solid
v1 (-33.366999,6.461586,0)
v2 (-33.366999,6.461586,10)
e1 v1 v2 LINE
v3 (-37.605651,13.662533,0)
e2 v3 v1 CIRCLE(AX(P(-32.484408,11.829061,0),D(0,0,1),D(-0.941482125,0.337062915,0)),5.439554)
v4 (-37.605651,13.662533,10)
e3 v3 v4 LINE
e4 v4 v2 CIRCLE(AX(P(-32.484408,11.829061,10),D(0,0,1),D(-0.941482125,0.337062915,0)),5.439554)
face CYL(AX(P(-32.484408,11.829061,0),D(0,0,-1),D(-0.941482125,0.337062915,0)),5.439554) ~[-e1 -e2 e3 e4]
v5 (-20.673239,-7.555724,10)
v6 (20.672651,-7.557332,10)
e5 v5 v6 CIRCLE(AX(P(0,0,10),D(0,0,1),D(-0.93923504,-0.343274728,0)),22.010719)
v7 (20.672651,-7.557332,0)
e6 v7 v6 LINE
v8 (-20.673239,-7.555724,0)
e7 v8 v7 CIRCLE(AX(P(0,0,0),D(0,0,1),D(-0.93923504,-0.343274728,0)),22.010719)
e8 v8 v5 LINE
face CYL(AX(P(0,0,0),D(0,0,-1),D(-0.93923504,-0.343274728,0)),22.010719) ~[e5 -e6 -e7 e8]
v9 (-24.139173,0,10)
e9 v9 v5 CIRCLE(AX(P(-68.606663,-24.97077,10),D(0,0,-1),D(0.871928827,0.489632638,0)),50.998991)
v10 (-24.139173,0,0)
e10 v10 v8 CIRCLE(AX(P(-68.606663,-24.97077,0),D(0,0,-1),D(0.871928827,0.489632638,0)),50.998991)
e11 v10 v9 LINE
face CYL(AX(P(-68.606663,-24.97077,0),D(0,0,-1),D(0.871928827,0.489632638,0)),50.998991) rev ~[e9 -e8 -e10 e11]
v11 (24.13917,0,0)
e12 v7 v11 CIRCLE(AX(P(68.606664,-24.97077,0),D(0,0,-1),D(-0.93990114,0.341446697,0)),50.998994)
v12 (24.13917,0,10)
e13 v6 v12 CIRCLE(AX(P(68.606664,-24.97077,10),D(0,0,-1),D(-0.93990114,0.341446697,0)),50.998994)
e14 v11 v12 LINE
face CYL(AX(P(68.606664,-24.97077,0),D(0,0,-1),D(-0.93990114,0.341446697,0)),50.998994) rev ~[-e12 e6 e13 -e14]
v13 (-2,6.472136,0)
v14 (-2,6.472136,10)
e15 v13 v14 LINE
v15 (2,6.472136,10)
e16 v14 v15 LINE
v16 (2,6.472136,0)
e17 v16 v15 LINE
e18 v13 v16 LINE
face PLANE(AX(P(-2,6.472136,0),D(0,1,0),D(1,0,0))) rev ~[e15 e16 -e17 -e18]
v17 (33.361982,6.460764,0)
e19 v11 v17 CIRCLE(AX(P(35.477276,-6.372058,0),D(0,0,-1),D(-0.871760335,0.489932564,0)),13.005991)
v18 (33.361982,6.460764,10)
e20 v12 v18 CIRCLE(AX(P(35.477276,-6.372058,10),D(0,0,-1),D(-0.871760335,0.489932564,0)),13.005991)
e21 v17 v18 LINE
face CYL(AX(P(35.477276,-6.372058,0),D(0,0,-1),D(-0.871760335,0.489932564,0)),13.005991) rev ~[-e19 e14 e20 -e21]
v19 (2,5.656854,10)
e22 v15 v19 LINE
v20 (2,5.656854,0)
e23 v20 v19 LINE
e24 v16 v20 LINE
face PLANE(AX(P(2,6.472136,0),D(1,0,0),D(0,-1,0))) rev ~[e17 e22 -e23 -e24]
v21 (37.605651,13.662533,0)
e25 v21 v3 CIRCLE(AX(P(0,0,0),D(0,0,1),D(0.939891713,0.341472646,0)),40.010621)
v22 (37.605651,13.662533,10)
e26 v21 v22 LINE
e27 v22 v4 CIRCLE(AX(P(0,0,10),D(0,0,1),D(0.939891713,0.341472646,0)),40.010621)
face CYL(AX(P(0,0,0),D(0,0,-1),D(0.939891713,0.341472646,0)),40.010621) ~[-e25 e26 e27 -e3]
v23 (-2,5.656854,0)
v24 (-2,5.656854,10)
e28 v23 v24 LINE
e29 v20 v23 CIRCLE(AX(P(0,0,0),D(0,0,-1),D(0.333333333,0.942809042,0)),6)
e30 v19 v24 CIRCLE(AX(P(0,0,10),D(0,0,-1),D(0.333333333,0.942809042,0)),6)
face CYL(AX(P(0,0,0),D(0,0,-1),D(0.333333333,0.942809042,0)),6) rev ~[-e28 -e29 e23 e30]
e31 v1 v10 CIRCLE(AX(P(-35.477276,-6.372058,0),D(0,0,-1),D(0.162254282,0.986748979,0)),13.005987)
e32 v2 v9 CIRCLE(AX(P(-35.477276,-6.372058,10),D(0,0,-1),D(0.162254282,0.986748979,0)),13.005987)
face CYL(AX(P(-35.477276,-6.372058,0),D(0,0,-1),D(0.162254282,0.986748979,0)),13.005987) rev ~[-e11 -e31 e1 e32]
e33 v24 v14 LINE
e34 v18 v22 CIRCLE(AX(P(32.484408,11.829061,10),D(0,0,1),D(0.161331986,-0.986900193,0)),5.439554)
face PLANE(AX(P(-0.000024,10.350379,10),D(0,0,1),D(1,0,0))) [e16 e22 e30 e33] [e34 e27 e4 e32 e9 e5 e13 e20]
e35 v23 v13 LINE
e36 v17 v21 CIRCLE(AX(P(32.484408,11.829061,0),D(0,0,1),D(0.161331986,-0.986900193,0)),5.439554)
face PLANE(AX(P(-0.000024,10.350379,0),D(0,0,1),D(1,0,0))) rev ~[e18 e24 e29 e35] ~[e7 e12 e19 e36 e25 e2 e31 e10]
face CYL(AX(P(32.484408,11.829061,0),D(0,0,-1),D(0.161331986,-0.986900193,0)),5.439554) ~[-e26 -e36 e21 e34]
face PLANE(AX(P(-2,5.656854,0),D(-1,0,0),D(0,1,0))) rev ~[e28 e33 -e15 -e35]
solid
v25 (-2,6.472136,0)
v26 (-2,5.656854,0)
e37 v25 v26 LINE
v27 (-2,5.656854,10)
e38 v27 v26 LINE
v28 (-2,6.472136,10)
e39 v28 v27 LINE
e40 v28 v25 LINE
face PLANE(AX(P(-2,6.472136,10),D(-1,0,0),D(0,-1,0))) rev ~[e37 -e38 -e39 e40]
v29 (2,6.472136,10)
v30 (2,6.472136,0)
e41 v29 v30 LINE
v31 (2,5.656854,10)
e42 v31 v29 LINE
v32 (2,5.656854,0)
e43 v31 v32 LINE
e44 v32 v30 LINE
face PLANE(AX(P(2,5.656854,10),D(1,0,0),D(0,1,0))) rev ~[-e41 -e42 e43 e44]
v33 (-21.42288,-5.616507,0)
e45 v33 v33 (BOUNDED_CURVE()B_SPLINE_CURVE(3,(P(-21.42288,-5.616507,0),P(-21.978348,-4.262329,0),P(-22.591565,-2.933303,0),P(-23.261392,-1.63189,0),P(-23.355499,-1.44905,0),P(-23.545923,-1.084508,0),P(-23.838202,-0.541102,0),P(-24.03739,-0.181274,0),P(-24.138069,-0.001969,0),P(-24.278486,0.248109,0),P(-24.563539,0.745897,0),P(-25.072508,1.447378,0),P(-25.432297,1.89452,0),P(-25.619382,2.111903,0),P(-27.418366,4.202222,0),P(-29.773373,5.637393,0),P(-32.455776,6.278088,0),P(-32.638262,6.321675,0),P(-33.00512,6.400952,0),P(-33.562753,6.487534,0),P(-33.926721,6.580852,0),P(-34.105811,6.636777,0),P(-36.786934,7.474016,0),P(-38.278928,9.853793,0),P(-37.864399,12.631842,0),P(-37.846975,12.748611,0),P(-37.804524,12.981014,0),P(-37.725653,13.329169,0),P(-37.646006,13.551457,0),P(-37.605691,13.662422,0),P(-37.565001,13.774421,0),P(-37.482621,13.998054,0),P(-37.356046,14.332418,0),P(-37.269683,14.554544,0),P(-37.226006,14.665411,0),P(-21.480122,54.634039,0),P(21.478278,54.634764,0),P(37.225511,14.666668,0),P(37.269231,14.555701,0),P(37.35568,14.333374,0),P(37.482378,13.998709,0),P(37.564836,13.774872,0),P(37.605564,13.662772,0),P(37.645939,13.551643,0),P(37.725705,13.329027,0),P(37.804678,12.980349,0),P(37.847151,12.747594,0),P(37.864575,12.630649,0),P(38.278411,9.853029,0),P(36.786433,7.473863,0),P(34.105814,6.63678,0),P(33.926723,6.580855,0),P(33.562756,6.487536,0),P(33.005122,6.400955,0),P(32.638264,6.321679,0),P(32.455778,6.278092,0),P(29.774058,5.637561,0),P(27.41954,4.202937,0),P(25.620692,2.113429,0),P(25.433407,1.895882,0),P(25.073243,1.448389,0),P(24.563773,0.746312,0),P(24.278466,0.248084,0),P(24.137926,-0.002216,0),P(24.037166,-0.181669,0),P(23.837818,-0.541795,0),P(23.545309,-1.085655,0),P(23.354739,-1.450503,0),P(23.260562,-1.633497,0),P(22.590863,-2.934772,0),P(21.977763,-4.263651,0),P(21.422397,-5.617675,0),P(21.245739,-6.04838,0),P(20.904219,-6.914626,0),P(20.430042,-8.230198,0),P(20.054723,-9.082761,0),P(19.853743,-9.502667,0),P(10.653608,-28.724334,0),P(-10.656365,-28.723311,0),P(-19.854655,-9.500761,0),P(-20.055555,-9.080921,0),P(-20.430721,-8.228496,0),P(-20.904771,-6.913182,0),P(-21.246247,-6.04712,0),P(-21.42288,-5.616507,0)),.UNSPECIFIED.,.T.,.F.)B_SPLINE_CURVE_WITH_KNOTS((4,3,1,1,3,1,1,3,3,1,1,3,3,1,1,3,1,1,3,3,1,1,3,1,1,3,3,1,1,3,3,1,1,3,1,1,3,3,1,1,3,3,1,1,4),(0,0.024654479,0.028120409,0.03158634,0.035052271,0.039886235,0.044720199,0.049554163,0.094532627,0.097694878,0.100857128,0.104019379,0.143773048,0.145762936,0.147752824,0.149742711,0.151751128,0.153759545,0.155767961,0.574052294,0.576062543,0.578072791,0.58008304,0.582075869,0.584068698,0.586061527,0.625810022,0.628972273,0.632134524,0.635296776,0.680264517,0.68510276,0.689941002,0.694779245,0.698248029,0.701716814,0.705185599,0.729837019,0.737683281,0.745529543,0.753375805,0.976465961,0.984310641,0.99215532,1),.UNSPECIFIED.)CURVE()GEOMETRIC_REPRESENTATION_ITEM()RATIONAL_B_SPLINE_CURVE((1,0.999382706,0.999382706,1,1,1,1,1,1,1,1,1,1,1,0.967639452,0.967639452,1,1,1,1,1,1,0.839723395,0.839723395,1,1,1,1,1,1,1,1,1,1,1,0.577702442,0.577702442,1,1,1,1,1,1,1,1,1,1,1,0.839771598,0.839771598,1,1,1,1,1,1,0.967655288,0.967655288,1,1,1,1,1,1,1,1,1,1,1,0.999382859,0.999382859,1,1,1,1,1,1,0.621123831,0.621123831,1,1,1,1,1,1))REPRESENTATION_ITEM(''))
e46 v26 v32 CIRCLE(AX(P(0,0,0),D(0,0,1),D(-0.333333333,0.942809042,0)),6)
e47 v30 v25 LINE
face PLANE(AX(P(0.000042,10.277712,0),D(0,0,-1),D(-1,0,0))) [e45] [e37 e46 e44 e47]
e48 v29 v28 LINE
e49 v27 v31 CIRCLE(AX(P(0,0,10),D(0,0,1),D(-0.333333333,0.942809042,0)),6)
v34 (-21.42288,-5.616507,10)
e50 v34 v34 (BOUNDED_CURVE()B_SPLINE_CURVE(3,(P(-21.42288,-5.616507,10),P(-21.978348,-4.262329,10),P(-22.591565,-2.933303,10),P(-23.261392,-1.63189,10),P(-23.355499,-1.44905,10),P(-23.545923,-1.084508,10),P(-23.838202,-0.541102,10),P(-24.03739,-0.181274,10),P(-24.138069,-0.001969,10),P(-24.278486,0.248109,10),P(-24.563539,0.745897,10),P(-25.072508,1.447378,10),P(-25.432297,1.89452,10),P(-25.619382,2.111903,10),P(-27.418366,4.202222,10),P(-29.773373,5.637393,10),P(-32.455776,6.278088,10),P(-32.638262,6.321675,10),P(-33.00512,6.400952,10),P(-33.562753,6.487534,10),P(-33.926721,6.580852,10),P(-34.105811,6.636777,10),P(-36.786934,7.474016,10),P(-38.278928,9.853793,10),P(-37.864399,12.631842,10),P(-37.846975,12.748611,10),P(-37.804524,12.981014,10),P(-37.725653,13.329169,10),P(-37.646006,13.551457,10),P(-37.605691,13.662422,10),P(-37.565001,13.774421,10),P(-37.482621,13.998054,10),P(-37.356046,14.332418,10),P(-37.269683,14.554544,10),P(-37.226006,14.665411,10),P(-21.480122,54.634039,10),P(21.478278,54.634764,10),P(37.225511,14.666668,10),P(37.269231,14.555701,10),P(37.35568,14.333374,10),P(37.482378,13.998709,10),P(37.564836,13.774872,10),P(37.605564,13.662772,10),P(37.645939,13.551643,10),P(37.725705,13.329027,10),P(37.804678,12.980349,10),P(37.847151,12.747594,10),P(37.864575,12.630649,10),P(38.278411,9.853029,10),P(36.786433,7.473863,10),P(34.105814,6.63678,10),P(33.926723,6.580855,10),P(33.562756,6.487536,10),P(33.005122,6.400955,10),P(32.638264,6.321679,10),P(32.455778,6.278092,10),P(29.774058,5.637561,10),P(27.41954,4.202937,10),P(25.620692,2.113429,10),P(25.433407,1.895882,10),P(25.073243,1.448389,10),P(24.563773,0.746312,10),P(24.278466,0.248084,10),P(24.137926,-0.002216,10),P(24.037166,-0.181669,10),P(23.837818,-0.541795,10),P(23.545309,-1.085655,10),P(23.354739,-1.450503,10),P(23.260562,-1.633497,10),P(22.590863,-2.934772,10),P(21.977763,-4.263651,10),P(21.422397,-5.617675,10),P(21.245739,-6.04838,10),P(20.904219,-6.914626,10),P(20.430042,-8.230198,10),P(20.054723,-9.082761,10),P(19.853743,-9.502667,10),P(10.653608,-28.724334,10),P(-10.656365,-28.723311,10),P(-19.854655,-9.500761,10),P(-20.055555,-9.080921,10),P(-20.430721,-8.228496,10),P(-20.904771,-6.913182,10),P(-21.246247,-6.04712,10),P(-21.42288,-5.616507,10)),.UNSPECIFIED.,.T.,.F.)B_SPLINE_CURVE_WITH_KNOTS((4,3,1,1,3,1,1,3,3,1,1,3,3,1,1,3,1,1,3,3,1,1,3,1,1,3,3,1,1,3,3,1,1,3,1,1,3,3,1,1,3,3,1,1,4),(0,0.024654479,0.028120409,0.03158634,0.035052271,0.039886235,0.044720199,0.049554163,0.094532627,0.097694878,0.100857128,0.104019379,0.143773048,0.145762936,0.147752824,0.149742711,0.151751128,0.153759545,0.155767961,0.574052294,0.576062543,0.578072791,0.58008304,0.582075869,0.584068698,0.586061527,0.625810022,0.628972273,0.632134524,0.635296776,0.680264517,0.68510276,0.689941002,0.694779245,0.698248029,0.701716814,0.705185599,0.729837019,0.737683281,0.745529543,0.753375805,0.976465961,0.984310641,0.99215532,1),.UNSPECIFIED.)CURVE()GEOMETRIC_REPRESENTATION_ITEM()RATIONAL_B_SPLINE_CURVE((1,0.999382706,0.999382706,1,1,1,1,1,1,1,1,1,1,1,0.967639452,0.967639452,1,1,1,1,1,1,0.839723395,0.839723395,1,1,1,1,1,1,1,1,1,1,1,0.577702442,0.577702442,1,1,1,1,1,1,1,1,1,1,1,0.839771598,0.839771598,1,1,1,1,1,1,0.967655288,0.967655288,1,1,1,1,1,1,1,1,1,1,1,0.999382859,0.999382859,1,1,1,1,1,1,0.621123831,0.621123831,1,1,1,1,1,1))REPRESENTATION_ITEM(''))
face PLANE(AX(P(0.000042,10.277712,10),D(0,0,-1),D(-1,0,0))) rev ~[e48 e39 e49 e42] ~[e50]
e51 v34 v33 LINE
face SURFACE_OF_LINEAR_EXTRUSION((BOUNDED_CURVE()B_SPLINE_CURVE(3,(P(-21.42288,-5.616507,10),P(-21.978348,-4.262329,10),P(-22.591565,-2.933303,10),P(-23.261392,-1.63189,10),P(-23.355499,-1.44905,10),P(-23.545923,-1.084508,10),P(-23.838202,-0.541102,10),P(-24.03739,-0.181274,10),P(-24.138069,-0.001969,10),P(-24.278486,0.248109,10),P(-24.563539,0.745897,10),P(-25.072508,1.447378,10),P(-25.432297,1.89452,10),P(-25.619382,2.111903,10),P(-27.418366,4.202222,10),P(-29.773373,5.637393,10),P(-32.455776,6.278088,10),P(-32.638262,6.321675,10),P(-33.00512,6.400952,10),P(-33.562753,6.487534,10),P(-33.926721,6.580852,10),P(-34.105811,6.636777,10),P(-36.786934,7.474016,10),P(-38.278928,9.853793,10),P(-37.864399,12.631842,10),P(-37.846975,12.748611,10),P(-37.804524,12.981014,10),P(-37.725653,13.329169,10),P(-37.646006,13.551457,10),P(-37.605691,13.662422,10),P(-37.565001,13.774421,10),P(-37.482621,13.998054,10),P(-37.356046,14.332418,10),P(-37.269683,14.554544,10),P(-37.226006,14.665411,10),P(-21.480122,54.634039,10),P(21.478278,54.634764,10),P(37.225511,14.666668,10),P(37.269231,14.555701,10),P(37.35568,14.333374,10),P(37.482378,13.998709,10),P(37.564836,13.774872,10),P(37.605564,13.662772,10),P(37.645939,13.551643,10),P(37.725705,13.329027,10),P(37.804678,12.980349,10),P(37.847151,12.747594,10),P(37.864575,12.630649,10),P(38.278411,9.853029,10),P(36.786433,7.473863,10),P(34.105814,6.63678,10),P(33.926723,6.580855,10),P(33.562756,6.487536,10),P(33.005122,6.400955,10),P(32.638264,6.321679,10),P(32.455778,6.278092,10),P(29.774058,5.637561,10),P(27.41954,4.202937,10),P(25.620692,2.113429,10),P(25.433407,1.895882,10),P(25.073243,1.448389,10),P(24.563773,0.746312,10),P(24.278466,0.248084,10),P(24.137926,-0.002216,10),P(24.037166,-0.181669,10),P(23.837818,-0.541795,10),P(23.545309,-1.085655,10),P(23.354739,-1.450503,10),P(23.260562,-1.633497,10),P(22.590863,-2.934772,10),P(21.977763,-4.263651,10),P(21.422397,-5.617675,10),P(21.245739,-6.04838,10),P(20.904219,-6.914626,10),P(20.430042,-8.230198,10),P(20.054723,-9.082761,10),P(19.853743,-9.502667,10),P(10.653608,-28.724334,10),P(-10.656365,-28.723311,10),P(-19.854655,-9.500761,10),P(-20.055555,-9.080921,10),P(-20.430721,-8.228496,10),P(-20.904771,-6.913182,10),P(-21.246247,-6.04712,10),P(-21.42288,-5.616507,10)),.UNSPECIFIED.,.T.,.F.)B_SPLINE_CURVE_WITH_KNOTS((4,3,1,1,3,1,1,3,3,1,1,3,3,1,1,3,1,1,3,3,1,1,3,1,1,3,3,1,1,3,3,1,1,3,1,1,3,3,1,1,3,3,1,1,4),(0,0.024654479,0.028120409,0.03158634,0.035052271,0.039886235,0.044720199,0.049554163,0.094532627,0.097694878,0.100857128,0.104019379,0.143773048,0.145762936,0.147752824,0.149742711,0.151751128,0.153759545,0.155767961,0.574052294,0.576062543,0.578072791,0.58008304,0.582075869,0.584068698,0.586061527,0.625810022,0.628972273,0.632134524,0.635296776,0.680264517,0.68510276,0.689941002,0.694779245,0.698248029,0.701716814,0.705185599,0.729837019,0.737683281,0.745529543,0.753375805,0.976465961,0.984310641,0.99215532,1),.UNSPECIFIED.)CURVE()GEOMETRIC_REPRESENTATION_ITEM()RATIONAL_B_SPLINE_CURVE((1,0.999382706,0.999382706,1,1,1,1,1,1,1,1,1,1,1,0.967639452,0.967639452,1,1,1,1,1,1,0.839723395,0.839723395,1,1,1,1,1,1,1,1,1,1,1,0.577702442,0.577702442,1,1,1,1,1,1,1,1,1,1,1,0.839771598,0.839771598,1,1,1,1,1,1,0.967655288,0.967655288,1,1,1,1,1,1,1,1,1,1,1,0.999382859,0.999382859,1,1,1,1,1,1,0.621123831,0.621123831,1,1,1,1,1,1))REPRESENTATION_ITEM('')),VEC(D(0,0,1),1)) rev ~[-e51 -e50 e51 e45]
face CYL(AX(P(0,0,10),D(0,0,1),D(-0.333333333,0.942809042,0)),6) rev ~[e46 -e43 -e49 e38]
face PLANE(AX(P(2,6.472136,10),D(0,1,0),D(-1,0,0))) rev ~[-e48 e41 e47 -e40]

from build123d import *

# Parameters (mm, degrees)
EXTRUDE_1_DEPTH = 10
EXTRUDE_2_DEPTH = 10


with BuildPart() as part:
    # 草图1 → 凸台-拉伸1 (new body)
    with BuildSketch(Plane.XY):
        with BuildLine():
            ThreePointArc((-20.67323893, -7.555723727), (-0.000856312, -22.010719392), (20.672650967, -7.557332261))
            ThreePointArc((20.672650967, -7.557332261), (22.251643113, -3.707904383), (24.139169609, 0))
            ThreePointArc((24.139169609, 0), (28.015114123, 4.280261917), (33.361982334, 6.460763761))
            ThreePointArc((33.361982334, 6.460763761), (37.170858971, 9.06755238), (37.605651194, 13.66253267))
            ThreePointArc((37.605651194, 13.66253267), (0, 40.010621099), (-37.605651194, 13.66253267))
            ThreePointArc((-37.605651194, 13.66253267), (-37.172148925, 9.069742682), (-33.366999211, 6.461586294))
            ThreePointArc((-33.366999211, 6.461586294), (-28.017198894, 4.281717924), (-24.139173474, 0))
            ThreePointArc((-24.139173474, 0), (-22.252003596, -3.707126596), (-20.67323893, -7.555723727))
        make_face()
        with BuildLine():
            Line((-2, 6.47213596), (2, 6.47213596))
            Line((2, 6.47213596), (2, 5.656854249))
            ThreePointArc((2, 5.656854249), (0, -6), (-2, 5.656854249))
            Line((-2, 5.656854249), (-2, 6.47213596))
        make_face(mode=Mode.SUBTRACT)
    extrude(amount=EXTRUDE_1_DEPTH)


with BuildPart() as body_2:
    # 草图2 → 凸台-拉伸2 (new body)
    with BuildSketch(Plane.XY.offset(10)):
        with BuildLine():
            add(Edge.make_bspline(
                [(-21.422879504, -5.616507247), (-21.978348411, -4.262328846), (-22.591564544, -2.933302577), (-23.261392298, -1.631889642), (-23.355498671, -1.449049726), (-23.545923141, -1.084508252), (-23.838202004, -0.541102033), (-24.037390022, -0.18127416), (-24.138068514, -0.001969153), (-24.278485684, 0.248109106), (-24.563539125, 0.745896628), (-25.072507629, 1.447378139), (-25.43229715, 1.894520131), (-25.619382376, 2.111902825), (-27.418365713, 4.202222035), (-29.773372852, 5.637393394), (-32.455775829, 6.278088107), (-32.638261709, 6.321675047), (-33.005119771, 6.400951526), (-33.562753418, 6.48753417), (-33.926720814, 6.58085246), (-34.105811106, 6.636777278), (-36.786933951, 7.474015891), (-38.278928257, 9.853793442), (-37.86439868, 12.631841936), (-37.846974871, 12.748610897), (-37.804524083, 12.981014304), (-37.725652679, 13.329169048), (-37.646005904, 13.551456702), (-37.605691369, 13.662422091), (-37.565001441, 13.774420742), (-37.482620912, 13.998054491), (-37.356046424, 14.332417645), (-37.269682862, 14.554543601), (-37.226005795, 14.665411459), (-21.48012174, 54.634039189), (21.478277518, 54.634764234), (37.225510733, 14.666668039), (37.269231391, 14.555700517), (37.355680339, 14.333374485), (37.482377524, 13.998708972), (37.564836202, 13.774872309), (37.605564291, 13.662771865), (37.645939449, 13.551642834), (37.725704566, 13.329026831), (37.804678054, 12.98034864), (37.847151228, 12.747593973), (37.864574858, 12.63064855), (38.278410711, 9.853029243), (36.786433101, 7.473863016), (34.105813592, 6.636779878), (33.9267233, 6.580854946), (33.562755888, 6.487536437), (33.005121852, 6.400955025), (32.638263705, 6.321678609), (32.455777783, 6.278091699), (29.774058016, 5.637560767), (27.419539773, 4.202937251), (25.620691698, 2.113428605), (25.433407249, 1.895882454), (25.073242833, 1.448389403), (24.56377311, 0.746311995), (24.278466412, 0.248084383), (24.137926355, -0.002216006), (24.037165969, -0.181669212), (23.837817743, -0.541795477), (23.545309299, -1.085655294), (23.354739155, -1.450502744), (23.260561787, -1.633496547), (22.59086337, -2.934771619), (21.977763421, -4.26365131), (21.422397048, -5.617675303), (21.245739446, -6.04837951), (20.904218814, -6.914625584), (20.430042275, -8.230197816), (20.054723433, -9.082761197), (19.85374254, -9.502666786), (10.653608089, -28.724334225), (-10.656365446, -28.723311395), (-19.854654662, -9.500760873), (-20.055554715, -9.080920691), (-20.430721402, -8.228495822), (-20.904771275, -6.913182123), (-21.246246862, -6.047120205), (-21.422879504, -5.616507247)],
                knots=[0, 0, 0, 0, 0.024654479, 0.024654479, 0.024654479, 0.028120409, 0.03158634, 0.035052271, 0.035052271, 0.035052271, 0.039886235, 0.044720199, 0.049554163, 0.049554163, 0.049554163, 0.094532627, 0.094532627, 0.094532627, 0.097694878, 0.100857128, 0.104019379, 0.104019379, 0.104019379, 0.143773048, 0.143773048, 0.143773048, 0.145762936, 0.147752824, 0.149742711, 0.149742711, 0.149742711, 0.151751128, 0.153759545, 0.155767961, 0.155767961, 0.155767961, 0.574052294, 0.574052294, 0.574052294, 0.576062543, 0.578072791, 0.58008304, 0.58008304, 0.58008304, 0.582075869, 0.584068698, 0.586061527, 0.586061527, 0.586061527, 0.625810022, 0.625810022, 0.625810022, 0.628972273, 0.632134524, 0.635296776, 0.635296776, 0.635296776, 0.680264517, 0.680264517, 0.680264517, 0.68510276, 0.689941002, 0.694779245, 0.694779245, 0.694779245, 0.698248029, 0.701716814, 0.705185599, 0.705185599, 0.705185599, 0.729837019, 0.729837019, 0.729837019, 0.737683281, 0.745529543, 0.753375805, 0.753375805, 0.753375805, 0.976465961, 0.976465961, 0.976465961, 0.984310641, 0.99215532, 1, 1, 1, 1], degree=3, weights=[1, 0.999382706, 0.999382706, 1, 1, 1, 1, 1, 1, 1, 1, 1, 1, 1, 0.967639452, 0.967639452, 1, 1, 1, 1, 1, 1, 0.839723395, 0.839723395, 1, 1, 1, 1, 1, 1, 1, 1, 1, 1, 1, 0.577702442, 0.577702442, 1, 1, 1, 1, 1, 1, 1, 1, 1, 1, 1, 0.839771598, 0.839771598, 1, 1, 1, 1, 1, 1, 0.967655288, 0.967655288, 1, 1, 1, 1, 1, 1, 1, 1, 1, 1, 1, 0.999382859, 0.999382859, 1, 1, 1, 1, 1, 1, 0.621123831, 0.621123831, 1, 1, 1, 1, 1, 1]))
        make_face()
        with BuildLine():
            Line((-2, 6.47213596), (-2, 5.656854249))
            ThreePointArc((-2, 5.656854249), (0, -6), (2, 5.656854249))
            Line((2, 5.656854249), (2, 6.47213596))
            Line((2, 6.47213596), (-2, 6.47213596))
        make_face(mode=Mode.SUBTRACT)
    extrude(amount=-EXTRUDE_2_DEPTH)


solid = Compound([part.part, body_2.part])
